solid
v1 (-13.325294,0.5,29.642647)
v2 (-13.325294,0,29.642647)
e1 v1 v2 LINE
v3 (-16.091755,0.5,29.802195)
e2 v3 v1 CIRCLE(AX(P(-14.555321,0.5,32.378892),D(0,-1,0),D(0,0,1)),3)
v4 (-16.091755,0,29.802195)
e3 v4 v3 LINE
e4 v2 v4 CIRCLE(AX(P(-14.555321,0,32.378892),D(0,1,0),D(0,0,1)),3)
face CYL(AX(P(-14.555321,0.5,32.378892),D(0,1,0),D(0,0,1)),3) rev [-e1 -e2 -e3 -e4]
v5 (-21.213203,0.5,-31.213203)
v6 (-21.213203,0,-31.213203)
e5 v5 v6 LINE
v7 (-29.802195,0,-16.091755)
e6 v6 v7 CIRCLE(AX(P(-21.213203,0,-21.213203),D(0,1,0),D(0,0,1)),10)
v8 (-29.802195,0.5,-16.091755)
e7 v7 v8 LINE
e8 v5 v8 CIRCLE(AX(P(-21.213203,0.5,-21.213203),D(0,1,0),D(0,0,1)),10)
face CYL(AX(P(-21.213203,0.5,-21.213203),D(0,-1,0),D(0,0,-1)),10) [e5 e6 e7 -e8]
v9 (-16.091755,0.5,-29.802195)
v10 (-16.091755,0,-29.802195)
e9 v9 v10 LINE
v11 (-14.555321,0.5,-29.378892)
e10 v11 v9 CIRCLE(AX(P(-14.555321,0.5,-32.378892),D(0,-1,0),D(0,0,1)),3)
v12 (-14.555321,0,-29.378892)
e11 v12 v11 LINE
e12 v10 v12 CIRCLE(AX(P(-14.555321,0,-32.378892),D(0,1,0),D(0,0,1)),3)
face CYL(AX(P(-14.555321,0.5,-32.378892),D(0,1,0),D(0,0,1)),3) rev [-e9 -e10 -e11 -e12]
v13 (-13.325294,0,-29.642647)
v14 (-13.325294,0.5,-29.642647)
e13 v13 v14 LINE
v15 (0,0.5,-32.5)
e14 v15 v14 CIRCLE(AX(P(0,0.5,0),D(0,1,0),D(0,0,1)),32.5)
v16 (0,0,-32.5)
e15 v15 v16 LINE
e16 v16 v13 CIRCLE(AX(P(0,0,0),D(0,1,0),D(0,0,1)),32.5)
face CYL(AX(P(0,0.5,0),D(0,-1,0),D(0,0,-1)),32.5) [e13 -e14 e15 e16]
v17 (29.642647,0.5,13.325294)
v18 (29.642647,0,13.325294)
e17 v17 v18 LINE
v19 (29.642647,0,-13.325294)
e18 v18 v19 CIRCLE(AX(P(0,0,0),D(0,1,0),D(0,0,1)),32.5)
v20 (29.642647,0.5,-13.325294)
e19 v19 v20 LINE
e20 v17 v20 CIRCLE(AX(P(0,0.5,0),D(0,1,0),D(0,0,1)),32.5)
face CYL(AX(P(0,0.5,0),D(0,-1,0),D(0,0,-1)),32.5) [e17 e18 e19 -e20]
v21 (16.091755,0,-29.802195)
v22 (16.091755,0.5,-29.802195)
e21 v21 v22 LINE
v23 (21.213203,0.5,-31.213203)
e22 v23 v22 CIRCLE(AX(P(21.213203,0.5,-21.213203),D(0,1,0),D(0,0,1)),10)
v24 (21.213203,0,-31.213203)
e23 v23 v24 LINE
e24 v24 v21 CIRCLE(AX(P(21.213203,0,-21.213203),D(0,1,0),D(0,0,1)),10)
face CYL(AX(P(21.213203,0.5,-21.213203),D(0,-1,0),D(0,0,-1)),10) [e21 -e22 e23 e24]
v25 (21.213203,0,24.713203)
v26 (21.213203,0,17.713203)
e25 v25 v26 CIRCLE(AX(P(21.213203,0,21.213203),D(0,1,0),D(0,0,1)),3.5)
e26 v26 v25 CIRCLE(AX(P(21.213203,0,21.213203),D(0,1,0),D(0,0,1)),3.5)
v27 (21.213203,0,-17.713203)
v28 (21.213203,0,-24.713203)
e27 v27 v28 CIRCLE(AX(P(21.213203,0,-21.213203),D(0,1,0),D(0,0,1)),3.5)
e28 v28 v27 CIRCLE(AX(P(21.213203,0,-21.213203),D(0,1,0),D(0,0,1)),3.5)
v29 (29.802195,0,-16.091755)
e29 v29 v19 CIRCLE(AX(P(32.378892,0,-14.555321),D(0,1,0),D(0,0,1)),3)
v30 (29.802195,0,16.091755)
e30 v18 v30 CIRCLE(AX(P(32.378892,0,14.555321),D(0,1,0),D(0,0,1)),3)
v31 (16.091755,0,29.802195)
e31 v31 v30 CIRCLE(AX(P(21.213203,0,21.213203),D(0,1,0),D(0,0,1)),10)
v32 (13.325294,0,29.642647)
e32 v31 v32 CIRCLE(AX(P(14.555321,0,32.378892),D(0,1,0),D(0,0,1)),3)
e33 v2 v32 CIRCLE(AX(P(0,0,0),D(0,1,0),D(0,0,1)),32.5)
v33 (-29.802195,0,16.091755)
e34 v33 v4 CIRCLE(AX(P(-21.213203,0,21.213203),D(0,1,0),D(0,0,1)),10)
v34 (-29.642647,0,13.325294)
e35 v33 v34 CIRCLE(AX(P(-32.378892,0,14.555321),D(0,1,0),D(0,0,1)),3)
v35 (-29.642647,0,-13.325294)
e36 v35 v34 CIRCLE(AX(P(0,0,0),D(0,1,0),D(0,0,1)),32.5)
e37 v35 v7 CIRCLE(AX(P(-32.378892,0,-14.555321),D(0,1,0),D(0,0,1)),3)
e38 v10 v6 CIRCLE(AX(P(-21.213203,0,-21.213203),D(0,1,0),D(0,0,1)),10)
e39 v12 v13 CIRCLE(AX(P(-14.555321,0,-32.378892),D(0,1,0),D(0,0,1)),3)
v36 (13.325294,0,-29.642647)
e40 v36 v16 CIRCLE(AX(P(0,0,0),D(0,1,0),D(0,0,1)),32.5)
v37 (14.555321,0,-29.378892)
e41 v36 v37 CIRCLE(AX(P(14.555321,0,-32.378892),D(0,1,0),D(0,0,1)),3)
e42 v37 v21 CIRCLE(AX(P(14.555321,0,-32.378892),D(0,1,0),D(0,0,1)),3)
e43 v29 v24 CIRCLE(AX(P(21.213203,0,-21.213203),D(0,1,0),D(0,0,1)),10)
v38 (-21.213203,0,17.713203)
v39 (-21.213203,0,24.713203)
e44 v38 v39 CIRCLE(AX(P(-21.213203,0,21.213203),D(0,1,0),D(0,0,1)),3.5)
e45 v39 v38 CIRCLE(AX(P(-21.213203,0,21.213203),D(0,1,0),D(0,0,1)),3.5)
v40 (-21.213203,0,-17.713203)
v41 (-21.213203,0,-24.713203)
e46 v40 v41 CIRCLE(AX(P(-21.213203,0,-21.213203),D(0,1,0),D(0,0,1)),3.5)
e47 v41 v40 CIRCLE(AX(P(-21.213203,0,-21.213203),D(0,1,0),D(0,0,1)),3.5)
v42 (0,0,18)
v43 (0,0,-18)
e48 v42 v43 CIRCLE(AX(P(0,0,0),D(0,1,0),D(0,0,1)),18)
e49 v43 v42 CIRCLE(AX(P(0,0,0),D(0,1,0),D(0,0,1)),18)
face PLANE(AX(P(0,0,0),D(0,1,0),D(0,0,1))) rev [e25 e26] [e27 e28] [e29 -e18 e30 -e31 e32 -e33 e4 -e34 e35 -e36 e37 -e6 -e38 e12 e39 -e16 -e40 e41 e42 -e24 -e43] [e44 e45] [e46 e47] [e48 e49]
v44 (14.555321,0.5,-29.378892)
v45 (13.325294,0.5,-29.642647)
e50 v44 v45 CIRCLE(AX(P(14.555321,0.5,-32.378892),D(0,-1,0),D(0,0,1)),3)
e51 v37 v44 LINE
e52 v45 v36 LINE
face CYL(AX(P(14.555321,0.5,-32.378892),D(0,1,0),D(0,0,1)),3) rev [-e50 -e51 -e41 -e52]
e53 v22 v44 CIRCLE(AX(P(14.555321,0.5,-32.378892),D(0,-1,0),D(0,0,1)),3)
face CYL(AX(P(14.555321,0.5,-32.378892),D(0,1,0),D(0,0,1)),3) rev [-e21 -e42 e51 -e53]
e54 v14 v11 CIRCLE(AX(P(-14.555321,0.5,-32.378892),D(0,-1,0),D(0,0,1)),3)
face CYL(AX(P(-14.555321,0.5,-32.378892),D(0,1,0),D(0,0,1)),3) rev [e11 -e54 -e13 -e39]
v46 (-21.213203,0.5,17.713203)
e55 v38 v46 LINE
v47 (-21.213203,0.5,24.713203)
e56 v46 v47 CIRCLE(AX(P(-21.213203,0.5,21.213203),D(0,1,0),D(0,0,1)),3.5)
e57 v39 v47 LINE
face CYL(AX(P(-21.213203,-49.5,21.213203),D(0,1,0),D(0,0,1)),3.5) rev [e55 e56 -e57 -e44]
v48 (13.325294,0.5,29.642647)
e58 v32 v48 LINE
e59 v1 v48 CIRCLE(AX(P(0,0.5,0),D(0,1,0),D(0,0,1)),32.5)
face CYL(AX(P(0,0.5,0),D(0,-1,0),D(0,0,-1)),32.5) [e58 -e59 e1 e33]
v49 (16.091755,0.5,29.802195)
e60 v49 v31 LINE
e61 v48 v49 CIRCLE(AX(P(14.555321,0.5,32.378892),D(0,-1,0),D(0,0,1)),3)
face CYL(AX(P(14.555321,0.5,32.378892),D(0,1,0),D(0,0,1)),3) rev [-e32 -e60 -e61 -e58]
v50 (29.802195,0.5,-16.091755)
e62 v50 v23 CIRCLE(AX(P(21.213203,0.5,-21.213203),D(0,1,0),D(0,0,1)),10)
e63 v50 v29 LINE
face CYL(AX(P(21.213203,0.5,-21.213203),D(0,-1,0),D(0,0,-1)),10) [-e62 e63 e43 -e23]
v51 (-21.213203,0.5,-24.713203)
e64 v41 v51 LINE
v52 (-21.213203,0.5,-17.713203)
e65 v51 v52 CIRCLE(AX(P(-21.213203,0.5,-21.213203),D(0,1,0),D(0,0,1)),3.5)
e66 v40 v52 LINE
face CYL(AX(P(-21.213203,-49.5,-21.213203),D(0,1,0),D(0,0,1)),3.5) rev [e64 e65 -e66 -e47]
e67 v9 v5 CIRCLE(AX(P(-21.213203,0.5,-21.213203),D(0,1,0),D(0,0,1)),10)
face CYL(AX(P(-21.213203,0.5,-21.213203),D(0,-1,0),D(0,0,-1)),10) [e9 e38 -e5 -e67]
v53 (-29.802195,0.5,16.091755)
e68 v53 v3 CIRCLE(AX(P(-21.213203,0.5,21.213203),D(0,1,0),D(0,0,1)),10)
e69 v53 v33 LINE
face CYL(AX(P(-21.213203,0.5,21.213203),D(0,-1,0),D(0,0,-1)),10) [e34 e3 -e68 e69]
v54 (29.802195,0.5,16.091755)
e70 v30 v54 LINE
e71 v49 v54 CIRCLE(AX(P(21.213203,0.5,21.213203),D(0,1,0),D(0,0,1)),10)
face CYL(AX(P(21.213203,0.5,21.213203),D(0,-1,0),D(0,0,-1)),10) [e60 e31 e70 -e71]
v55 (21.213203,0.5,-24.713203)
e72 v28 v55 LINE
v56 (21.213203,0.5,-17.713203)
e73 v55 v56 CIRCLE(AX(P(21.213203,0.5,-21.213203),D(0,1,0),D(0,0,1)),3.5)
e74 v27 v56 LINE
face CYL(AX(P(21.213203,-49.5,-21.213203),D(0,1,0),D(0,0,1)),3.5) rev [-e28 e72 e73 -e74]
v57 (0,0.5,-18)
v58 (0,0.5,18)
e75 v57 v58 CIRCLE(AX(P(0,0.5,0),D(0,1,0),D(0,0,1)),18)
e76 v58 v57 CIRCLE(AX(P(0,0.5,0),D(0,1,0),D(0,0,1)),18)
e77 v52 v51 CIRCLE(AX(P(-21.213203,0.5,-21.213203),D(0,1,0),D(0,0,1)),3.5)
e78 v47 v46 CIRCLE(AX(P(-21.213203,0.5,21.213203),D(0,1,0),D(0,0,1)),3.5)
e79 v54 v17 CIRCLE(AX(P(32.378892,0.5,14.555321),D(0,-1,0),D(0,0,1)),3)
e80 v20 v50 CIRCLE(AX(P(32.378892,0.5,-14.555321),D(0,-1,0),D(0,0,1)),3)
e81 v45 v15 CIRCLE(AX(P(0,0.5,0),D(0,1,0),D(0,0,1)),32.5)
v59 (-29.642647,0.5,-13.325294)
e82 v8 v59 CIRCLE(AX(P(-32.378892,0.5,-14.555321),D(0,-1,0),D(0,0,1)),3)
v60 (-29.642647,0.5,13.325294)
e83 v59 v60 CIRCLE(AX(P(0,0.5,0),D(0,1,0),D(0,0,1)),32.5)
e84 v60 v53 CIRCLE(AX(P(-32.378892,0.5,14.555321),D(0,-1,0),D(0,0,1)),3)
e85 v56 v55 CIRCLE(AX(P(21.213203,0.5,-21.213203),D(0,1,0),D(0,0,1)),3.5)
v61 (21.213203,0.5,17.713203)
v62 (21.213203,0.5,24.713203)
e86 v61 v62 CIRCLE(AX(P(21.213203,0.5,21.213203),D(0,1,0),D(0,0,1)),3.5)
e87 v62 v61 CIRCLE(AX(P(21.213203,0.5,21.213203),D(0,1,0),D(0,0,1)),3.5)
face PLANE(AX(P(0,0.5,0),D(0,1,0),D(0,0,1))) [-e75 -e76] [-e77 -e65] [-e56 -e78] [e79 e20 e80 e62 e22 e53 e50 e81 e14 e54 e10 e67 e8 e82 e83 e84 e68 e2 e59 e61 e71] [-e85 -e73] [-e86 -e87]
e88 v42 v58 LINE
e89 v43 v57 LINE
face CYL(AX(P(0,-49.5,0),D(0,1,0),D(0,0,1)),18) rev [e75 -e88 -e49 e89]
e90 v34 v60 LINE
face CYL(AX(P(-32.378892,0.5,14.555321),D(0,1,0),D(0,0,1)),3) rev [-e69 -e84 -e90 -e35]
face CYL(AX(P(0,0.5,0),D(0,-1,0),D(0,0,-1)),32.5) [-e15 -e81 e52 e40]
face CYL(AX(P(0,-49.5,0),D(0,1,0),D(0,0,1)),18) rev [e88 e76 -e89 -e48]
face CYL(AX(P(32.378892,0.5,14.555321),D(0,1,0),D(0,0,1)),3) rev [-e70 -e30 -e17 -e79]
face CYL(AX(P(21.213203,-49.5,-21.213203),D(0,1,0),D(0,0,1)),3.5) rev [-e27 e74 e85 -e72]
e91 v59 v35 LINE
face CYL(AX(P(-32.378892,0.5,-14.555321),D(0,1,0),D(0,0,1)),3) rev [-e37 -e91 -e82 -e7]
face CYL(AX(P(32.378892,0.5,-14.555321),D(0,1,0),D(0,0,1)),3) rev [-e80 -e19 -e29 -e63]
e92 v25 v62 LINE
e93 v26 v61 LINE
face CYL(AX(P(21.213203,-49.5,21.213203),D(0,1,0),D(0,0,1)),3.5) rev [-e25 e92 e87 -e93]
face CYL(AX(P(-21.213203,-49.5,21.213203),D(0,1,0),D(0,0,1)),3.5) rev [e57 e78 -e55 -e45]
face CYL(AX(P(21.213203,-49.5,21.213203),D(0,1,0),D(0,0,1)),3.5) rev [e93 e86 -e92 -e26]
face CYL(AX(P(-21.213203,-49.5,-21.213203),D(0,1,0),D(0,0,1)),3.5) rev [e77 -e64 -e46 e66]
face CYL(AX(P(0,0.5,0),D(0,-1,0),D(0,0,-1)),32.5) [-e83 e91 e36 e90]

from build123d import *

# Parameters (mm, degrees)
SKETCH1_R           = 10
SKETCH1_R_2         = 32.5
BOSS_EXTRUDE1_DEPTH = 0.5
SKETCH2_R           = 18
SKETCH2_R_2         = 3.5
CUT_EXTRUDE1_DEPTH  = 50
FILLET1_R           = 3


with BuildPart() as part:
    # Sketch1 → Boss-Extrude1 (new body)
    with BuildSketch(Plane(origin=(0, 0, 0), x_dir=(1, 0, 0), z_dir=(0, 1, 0))):
        with Locations((-21.213203436, -21.213203436)):
            Circle(SKETCH1_R)
        Circle(SKETCH1_R_2)
        with Locations((21.213203436, -21.213203436)):
            Circle(SKETCH1_R)
        with Locations((21.213203436, 21.213203436)):
            Circle(SKETCH1_R)
        with Locations((-21.213203436, 21.213203436)):
            Circle(SKETCH1_R)
    extrude(amount=BOSS_EXTRUDE1_DEPTH)

    # Sketch2 → Cut-Extrude1 (cut)
    with BuildSketch(Plane(origin=(0, 0.5, 0), x_dir=(1, 0, 0), z_dir=(0, 1, 0))):
        with Locations(Location((0, 0, 0), (0, 0, 270))):
            Circle(SKETCH2_R)
        with Locations(Location((21.213203436, 21.213203436, 0), (0, 0, 270))):
            Circle(SKETCH2_R_2)
        with Locations(Location((21.213203436, -21.213203436, 0), (0, 0, 270))):
            Circle(SKETCH2_R_2)
        with Locations(Location((-21.213203436, -21.213203436, 0), (0, 0, 270))):
            Circle(SKETCH2_R_2)
        with Locations(Location((-21.213203436, 21.213203436, 0), (0, 0, 270))):
            Circle(SKETCH2_R_2)
    extrude(amount=-CUT_EXTRUDE1_DEPTH, mode=Mode.SUBTRACT)

    # Fillet1
    fillet1_edges = [part.edges().sort_by_distance(p)[0] for p in [
        (-28.916041247, 0.25, -14.836190839),
        (-14.836190839, 0.25, -28.916041247),
        (14.836190839, 0.25, -28.916041247),
        (28.916041247, 0.25, -14.836190839),
        (28.916041247, 0.25, 14.836190839),
        (14.836190839, 0.25, 28.916041247),
        (-14.836190839, 0.25, 28.916041247),
        (-28.916041247, 0.25, 14.836190839),
    ]]
    fillet(fillet1_edges, radius=FILLET1_R)


solid = part.part
